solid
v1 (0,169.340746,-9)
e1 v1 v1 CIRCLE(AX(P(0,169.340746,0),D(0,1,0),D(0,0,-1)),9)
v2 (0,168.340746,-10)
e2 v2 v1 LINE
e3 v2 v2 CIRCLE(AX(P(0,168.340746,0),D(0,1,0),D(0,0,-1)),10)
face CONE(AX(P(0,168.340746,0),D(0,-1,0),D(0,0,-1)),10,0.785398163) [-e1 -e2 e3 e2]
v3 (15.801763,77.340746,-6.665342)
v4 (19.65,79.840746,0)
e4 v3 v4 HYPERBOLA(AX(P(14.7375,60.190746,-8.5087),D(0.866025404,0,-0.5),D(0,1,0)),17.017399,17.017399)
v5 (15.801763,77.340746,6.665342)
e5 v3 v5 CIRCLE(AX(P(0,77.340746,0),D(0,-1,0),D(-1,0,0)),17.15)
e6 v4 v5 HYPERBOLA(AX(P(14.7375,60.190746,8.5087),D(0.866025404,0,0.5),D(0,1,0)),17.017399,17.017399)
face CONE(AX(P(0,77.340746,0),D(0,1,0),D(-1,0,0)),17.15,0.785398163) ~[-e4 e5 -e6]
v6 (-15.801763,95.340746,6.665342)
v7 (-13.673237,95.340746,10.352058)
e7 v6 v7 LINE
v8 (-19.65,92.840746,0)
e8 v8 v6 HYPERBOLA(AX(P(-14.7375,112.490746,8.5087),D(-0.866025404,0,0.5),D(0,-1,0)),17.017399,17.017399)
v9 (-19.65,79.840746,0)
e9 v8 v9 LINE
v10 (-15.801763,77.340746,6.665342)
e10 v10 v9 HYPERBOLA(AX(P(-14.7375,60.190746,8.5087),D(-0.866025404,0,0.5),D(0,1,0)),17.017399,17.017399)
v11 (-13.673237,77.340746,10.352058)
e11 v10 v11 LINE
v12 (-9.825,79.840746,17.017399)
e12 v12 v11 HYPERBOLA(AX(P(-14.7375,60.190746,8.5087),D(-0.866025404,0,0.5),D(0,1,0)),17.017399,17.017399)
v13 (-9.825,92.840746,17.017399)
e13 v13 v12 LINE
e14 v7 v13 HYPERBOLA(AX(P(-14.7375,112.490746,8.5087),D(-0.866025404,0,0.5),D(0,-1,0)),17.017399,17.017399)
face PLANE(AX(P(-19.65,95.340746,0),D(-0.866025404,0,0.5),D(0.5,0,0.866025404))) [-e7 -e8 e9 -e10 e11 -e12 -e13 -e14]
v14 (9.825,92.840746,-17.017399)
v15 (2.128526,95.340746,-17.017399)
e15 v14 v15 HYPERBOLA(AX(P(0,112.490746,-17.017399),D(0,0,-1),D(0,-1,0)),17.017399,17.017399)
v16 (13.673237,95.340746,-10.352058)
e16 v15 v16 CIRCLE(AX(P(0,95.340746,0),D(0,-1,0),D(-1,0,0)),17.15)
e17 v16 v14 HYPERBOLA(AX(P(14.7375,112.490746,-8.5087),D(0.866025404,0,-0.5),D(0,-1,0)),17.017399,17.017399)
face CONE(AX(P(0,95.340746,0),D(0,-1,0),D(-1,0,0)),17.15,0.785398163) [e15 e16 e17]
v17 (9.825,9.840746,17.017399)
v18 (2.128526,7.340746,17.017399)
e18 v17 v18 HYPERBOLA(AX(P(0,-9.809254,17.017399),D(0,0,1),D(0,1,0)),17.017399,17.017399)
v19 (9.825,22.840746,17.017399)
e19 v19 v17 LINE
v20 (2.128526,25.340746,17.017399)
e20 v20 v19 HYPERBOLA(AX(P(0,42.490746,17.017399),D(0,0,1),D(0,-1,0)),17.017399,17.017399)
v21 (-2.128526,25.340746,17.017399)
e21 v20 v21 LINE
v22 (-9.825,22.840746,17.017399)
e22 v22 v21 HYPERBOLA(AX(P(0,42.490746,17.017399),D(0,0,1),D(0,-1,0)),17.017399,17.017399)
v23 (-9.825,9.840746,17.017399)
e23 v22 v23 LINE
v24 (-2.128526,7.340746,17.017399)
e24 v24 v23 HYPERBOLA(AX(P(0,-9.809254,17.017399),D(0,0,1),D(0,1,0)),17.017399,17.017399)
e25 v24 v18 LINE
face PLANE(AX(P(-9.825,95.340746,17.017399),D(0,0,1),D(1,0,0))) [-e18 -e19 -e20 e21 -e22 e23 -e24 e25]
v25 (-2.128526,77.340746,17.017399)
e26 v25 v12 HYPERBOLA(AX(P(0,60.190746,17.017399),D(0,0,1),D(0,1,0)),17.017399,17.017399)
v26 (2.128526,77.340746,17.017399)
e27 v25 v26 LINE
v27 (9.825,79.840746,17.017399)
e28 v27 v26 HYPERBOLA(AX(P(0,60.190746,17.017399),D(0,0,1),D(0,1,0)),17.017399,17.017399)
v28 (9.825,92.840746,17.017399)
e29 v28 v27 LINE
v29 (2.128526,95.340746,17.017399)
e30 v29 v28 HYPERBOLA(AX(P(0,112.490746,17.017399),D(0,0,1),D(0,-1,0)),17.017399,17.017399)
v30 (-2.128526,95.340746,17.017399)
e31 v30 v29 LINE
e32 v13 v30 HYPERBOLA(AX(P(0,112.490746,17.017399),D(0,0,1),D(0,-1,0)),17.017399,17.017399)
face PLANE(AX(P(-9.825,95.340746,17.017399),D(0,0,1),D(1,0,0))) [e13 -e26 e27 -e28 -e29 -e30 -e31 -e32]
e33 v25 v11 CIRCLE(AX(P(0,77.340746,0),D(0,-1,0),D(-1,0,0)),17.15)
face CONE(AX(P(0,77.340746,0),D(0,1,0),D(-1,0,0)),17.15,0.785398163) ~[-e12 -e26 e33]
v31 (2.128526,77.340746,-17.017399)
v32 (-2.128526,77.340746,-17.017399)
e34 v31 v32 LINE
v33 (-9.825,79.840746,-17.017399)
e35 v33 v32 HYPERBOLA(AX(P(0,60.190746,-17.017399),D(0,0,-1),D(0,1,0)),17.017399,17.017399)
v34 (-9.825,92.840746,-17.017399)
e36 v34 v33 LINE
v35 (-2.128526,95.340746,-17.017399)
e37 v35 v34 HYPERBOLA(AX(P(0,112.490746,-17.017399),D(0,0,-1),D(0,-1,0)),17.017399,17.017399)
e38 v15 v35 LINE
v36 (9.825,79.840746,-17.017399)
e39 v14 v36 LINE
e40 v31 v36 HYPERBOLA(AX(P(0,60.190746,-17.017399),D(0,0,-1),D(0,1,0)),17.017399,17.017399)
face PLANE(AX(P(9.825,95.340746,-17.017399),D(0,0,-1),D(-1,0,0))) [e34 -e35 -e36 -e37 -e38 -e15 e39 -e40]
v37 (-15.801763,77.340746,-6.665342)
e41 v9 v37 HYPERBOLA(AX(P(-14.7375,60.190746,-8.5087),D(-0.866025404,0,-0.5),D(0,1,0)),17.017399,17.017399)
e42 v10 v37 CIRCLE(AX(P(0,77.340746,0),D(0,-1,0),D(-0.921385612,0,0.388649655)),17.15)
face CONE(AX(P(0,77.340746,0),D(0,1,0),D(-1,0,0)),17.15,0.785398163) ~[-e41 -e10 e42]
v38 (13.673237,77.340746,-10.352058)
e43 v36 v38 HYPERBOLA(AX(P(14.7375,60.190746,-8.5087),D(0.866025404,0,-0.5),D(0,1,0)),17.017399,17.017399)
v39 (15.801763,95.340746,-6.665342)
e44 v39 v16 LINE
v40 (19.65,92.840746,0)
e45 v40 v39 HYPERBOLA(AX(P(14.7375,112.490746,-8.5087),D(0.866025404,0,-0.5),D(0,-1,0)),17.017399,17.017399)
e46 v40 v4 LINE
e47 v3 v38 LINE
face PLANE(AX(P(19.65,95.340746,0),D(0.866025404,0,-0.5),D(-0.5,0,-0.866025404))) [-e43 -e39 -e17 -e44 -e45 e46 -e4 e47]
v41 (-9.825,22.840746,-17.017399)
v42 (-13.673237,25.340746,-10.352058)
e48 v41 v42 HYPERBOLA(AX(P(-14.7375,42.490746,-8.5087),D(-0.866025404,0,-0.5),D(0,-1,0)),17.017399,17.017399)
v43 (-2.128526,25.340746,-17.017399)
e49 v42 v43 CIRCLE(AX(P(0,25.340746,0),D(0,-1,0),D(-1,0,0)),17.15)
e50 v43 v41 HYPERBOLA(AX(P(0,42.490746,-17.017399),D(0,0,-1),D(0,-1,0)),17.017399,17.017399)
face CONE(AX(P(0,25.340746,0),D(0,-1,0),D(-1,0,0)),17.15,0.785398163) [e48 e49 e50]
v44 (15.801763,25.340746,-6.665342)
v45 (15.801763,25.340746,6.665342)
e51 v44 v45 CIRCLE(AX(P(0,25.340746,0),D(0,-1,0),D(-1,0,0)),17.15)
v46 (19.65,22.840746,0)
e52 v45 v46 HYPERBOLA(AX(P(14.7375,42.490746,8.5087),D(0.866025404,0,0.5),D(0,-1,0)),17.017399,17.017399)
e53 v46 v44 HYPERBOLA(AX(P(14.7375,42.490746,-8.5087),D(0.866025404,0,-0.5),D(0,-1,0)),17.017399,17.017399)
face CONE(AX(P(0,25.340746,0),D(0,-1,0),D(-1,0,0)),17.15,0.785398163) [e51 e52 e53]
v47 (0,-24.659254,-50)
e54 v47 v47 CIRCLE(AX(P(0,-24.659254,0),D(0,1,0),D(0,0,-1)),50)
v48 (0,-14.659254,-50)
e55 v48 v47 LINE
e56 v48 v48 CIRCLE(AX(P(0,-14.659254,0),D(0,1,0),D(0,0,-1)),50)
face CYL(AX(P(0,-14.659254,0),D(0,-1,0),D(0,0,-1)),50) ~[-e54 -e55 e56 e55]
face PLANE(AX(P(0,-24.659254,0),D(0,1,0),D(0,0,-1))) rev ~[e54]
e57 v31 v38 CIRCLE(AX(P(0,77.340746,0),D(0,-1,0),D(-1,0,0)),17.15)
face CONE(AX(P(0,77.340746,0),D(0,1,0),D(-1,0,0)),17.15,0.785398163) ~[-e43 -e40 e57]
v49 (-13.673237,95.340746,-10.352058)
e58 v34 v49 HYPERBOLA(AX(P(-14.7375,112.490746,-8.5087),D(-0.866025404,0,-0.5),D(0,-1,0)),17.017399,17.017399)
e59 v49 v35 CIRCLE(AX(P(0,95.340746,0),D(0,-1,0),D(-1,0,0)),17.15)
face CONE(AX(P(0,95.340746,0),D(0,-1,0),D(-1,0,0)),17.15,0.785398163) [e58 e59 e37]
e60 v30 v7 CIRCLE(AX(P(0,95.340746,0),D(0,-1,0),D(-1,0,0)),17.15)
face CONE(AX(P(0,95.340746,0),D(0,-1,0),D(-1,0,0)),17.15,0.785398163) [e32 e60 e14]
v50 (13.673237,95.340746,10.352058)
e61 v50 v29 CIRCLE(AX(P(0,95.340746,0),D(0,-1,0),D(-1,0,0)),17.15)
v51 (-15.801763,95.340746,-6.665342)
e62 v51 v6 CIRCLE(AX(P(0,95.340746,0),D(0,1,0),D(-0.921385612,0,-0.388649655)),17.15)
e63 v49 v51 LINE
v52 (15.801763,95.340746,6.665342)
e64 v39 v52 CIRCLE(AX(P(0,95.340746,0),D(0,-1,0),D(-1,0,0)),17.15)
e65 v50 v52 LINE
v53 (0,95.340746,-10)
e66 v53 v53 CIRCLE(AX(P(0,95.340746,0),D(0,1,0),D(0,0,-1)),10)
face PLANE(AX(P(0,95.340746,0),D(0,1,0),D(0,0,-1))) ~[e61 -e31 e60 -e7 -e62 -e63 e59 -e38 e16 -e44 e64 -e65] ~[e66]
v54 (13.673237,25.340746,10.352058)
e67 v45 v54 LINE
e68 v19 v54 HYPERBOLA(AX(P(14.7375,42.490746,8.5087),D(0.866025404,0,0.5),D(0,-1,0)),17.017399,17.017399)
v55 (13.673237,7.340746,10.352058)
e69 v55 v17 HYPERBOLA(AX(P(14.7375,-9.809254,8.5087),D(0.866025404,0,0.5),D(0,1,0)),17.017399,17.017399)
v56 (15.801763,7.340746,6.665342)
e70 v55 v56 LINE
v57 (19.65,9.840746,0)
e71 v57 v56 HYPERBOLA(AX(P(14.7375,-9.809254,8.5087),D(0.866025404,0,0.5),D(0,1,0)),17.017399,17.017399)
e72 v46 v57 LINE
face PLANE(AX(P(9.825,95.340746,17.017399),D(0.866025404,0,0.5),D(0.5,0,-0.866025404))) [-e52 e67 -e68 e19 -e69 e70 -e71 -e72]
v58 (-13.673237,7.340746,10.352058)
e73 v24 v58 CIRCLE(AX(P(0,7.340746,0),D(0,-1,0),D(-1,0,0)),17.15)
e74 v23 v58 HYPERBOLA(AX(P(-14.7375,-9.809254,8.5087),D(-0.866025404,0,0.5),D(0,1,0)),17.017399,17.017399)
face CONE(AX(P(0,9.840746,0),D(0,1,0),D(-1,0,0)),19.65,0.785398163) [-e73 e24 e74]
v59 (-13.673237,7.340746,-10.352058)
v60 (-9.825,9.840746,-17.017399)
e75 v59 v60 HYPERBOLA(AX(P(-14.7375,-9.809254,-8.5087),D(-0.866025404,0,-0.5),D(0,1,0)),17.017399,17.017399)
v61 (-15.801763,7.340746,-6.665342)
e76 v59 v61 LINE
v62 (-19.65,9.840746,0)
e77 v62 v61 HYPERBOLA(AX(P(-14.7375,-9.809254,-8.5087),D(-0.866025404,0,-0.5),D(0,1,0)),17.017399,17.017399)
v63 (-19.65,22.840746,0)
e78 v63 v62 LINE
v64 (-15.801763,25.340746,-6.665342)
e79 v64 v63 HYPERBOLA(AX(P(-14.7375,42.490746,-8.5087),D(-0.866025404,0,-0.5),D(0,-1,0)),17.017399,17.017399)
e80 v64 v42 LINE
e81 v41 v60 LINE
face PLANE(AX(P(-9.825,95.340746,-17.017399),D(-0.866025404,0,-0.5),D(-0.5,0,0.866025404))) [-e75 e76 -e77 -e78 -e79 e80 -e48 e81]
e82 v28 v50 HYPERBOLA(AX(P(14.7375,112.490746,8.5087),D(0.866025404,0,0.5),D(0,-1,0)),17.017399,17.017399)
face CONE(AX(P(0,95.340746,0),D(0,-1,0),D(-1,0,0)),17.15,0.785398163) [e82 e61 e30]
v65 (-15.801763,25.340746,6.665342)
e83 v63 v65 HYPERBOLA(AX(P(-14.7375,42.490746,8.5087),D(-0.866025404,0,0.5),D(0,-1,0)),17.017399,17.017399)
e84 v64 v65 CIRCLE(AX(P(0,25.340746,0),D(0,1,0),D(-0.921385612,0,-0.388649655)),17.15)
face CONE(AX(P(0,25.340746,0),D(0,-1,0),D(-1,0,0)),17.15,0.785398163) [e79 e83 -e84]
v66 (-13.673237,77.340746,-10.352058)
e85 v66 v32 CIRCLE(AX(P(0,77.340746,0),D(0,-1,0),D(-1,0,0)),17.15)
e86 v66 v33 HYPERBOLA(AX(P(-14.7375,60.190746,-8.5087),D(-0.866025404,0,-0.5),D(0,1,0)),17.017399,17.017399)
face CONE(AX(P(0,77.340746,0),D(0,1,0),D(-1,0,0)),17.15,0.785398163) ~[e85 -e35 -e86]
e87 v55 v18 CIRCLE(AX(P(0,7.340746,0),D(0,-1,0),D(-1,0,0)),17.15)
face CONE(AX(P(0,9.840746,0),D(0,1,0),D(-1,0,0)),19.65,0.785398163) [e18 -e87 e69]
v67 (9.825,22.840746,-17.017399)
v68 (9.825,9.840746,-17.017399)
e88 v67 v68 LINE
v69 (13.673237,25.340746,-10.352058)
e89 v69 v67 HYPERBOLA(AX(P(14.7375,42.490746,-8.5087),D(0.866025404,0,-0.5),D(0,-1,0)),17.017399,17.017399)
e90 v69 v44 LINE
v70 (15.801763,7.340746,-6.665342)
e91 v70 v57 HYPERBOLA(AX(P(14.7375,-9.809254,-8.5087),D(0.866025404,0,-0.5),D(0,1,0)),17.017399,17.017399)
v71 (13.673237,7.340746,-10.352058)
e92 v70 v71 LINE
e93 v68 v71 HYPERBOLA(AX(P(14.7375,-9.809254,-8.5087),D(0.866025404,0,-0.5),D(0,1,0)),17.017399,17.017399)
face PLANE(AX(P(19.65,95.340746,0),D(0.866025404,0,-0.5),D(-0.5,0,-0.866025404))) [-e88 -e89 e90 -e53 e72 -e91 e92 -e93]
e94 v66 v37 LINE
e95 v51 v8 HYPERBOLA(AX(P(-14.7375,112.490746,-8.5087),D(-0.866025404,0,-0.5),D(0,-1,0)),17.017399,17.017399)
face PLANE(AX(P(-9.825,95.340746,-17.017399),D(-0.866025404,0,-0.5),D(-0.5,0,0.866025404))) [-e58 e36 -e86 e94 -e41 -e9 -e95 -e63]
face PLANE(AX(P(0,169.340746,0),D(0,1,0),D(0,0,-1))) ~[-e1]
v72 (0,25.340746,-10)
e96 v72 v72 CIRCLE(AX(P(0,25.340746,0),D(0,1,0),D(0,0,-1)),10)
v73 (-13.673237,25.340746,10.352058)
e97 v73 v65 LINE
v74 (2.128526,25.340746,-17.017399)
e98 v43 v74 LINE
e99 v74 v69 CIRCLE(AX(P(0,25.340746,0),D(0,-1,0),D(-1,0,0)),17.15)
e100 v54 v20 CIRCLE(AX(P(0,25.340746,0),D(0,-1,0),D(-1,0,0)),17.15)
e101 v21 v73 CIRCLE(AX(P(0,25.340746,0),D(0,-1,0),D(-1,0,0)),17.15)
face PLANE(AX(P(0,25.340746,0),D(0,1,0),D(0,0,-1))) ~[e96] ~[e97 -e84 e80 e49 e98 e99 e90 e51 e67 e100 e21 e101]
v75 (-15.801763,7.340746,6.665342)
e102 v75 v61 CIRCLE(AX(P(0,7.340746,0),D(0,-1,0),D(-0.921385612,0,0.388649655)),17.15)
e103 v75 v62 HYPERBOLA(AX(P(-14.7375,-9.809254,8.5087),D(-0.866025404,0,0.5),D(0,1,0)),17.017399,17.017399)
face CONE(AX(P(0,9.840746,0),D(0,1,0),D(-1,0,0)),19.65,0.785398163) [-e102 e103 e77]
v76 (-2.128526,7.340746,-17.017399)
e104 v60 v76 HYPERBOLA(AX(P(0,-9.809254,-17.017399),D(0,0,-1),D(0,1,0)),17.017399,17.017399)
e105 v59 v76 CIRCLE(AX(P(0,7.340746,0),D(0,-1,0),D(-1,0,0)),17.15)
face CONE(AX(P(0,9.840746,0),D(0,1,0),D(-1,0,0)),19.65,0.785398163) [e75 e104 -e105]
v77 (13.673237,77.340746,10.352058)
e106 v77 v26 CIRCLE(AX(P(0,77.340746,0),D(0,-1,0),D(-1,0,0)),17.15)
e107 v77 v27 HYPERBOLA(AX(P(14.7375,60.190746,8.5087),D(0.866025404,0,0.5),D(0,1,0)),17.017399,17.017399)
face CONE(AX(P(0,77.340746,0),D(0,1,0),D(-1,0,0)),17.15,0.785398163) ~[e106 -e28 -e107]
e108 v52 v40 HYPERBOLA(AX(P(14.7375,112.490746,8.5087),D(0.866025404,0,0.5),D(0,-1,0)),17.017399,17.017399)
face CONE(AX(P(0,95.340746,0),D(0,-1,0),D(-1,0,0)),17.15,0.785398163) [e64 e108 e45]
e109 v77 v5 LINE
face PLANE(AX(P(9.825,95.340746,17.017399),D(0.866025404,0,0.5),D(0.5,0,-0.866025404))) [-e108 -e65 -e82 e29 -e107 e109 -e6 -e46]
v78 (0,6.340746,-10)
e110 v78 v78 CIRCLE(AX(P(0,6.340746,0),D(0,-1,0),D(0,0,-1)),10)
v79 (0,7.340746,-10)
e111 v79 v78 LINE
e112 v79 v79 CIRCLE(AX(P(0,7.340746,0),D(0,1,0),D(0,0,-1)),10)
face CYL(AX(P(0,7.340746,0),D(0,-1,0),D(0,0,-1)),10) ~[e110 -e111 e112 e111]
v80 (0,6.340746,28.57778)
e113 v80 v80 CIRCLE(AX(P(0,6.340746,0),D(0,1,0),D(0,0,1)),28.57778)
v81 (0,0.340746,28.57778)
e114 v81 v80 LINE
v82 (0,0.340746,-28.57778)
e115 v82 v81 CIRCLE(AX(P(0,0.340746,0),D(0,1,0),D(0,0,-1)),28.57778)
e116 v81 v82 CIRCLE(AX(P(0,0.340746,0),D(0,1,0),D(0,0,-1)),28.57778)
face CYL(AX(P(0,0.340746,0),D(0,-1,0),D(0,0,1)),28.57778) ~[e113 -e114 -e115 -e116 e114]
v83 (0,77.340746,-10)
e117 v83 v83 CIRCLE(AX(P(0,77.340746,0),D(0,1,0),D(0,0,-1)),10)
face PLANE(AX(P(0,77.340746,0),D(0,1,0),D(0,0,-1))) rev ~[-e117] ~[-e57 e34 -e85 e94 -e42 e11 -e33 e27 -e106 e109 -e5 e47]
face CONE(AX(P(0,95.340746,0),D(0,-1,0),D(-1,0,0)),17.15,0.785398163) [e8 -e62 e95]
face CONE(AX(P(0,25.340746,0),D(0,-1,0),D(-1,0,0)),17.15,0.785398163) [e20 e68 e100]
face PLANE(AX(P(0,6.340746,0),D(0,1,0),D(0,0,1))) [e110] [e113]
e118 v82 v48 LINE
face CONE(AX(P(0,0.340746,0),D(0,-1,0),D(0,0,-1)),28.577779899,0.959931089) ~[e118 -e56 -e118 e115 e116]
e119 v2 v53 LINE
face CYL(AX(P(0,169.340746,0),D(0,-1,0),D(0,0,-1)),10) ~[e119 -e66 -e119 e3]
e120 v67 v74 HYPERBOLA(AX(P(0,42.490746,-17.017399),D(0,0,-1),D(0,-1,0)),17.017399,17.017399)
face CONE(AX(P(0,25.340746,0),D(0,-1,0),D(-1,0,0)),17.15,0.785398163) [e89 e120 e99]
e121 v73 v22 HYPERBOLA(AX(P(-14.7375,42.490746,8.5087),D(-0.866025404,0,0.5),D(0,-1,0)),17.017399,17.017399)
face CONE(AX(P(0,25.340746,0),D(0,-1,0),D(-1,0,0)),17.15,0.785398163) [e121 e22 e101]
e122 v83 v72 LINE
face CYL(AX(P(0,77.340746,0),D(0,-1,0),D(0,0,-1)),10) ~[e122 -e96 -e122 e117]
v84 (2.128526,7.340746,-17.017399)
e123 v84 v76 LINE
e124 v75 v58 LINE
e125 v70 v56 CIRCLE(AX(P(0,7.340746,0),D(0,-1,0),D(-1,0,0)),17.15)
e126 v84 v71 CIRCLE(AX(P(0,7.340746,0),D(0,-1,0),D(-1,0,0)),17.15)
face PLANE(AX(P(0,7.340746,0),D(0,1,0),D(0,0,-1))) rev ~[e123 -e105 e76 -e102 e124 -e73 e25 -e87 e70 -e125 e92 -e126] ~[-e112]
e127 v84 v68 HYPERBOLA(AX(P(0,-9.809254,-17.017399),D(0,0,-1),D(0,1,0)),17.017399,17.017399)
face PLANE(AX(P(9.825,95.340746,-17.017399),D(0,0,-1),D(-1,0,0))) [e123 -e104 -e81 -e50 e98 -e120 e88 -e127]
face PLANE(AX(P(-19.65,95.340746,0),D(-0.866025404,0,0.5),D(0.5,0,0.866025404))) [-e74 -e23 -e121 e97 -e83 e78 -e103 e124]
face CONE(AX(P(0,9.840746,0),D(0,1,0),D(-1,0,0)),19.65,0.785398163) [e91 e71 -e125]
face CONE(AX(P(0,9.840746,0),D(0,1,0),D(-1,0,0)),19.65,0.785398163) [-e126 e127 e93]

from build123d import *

# Parameters (mm, degrees)
SKETCH_2_R          = 28.577779899
EXTRUDE_1_DEPTH     = 6
SKETCH_4_R          = 24.484212217
CUT_EXTRUDE_5_DEPTH = 88
CHAMFER_1_SIZE      = 1


with BuildPart() as part:
    # 草图1 → 旋转1 (revolve)
    with BuildSketch(Plane.XY, mode=Mode.PRIVATE) as revolve_1_sk:
        Polygon((10, 169.340745793), (10, 95.340745793), (19.65, 95.340745793), (19.65, 77.340745793), (10, 77.340745793), (10, 25.340745793), (19.65, 25.340745793), (19.65, 7.340745793), (10, 7.340745793), (10, 0.340745793), (28.577779899, 0.340745793), (50, -14.659254207), (50, -24.659254207), (0, -24.659254207), (0, 169.340745793), align=None)
    revolve(revolve_1_sk.sketch.rotate(Axis((0, -29.818093999, 0), (0, 1, 0)), 90), axis=Axis((0, -29.818093999, 0), (0, 1, 0)))

    # 草图2 → 凸台-拉伸1 (add)
    with BuildSketch(Plane(origin=(0, 0.340745793, 0), x_dir=(1, 0, 0), z_dir=(0, 1, 0))):
        with Locations(Location((0, 0, 0), (0, 0, 270))):
            Circle(SKETCH_2_R)
    extrude(amount=EXTRUDE_1_DEPTH)

    # 草图4 → 切除-拉伸5 (cut)
    with BuildSketch(Plane(origin=(0, 95.340745793, 0), x_dir=(1, 0, 0), z_dir=(0, 1, 0))):
        Circle(SKETCH_4_R)
        Polygon((19.65, 0), (9.825, 17.017399184), (-9.825, 17.017399184), (-19.65, 0), (-9.825, -17.017399184), (9.825, -17.017399184), align=None, mode=Mode.SUBTRACT)
    extrude(amount=-CUT_EXTRUDE_5_DEPTH, mode=Mode.SUBTRACT)

    # 草图5 → 切除-旋转1 (revolve, cut)
    with BuildSketch(Plane.XY):
        Polygon((-17.15, 95.340745793), (-19.65, 92.840745793), (-26.926915052, 99.124494225), (-16.245783772, 99.906767383), align=None)
        Polygon((-17.15, 77.340745793), (-19.65, 79.840745793), (-19.65, 76.234905644), align=None)
        Polygon((-17.15, 25.340745793), (-19.65, 22.840745793), (-41.601041536, 16.623626451), (-25.840347108, 26.762569484), align=None)
        Polygon((-19.65, 9.840745793), (-17.15, 7.340745793), (-28.367472728, 7.340745793), align=None)
    revolve(axis=Axis((0, 180.885465797, 0), (0, -1, 0)), mode=Mode.SUBTRACT)

    # 倒角1
    chamfer_1_edges = [part.edges().sort_by_distance(p)[0] for p in [
        (0, 169.340745793, 10),
    ]]
    chamfer(chamfer_1_edges, length=CHAMFER_1_SIZE)


solid = part.part
